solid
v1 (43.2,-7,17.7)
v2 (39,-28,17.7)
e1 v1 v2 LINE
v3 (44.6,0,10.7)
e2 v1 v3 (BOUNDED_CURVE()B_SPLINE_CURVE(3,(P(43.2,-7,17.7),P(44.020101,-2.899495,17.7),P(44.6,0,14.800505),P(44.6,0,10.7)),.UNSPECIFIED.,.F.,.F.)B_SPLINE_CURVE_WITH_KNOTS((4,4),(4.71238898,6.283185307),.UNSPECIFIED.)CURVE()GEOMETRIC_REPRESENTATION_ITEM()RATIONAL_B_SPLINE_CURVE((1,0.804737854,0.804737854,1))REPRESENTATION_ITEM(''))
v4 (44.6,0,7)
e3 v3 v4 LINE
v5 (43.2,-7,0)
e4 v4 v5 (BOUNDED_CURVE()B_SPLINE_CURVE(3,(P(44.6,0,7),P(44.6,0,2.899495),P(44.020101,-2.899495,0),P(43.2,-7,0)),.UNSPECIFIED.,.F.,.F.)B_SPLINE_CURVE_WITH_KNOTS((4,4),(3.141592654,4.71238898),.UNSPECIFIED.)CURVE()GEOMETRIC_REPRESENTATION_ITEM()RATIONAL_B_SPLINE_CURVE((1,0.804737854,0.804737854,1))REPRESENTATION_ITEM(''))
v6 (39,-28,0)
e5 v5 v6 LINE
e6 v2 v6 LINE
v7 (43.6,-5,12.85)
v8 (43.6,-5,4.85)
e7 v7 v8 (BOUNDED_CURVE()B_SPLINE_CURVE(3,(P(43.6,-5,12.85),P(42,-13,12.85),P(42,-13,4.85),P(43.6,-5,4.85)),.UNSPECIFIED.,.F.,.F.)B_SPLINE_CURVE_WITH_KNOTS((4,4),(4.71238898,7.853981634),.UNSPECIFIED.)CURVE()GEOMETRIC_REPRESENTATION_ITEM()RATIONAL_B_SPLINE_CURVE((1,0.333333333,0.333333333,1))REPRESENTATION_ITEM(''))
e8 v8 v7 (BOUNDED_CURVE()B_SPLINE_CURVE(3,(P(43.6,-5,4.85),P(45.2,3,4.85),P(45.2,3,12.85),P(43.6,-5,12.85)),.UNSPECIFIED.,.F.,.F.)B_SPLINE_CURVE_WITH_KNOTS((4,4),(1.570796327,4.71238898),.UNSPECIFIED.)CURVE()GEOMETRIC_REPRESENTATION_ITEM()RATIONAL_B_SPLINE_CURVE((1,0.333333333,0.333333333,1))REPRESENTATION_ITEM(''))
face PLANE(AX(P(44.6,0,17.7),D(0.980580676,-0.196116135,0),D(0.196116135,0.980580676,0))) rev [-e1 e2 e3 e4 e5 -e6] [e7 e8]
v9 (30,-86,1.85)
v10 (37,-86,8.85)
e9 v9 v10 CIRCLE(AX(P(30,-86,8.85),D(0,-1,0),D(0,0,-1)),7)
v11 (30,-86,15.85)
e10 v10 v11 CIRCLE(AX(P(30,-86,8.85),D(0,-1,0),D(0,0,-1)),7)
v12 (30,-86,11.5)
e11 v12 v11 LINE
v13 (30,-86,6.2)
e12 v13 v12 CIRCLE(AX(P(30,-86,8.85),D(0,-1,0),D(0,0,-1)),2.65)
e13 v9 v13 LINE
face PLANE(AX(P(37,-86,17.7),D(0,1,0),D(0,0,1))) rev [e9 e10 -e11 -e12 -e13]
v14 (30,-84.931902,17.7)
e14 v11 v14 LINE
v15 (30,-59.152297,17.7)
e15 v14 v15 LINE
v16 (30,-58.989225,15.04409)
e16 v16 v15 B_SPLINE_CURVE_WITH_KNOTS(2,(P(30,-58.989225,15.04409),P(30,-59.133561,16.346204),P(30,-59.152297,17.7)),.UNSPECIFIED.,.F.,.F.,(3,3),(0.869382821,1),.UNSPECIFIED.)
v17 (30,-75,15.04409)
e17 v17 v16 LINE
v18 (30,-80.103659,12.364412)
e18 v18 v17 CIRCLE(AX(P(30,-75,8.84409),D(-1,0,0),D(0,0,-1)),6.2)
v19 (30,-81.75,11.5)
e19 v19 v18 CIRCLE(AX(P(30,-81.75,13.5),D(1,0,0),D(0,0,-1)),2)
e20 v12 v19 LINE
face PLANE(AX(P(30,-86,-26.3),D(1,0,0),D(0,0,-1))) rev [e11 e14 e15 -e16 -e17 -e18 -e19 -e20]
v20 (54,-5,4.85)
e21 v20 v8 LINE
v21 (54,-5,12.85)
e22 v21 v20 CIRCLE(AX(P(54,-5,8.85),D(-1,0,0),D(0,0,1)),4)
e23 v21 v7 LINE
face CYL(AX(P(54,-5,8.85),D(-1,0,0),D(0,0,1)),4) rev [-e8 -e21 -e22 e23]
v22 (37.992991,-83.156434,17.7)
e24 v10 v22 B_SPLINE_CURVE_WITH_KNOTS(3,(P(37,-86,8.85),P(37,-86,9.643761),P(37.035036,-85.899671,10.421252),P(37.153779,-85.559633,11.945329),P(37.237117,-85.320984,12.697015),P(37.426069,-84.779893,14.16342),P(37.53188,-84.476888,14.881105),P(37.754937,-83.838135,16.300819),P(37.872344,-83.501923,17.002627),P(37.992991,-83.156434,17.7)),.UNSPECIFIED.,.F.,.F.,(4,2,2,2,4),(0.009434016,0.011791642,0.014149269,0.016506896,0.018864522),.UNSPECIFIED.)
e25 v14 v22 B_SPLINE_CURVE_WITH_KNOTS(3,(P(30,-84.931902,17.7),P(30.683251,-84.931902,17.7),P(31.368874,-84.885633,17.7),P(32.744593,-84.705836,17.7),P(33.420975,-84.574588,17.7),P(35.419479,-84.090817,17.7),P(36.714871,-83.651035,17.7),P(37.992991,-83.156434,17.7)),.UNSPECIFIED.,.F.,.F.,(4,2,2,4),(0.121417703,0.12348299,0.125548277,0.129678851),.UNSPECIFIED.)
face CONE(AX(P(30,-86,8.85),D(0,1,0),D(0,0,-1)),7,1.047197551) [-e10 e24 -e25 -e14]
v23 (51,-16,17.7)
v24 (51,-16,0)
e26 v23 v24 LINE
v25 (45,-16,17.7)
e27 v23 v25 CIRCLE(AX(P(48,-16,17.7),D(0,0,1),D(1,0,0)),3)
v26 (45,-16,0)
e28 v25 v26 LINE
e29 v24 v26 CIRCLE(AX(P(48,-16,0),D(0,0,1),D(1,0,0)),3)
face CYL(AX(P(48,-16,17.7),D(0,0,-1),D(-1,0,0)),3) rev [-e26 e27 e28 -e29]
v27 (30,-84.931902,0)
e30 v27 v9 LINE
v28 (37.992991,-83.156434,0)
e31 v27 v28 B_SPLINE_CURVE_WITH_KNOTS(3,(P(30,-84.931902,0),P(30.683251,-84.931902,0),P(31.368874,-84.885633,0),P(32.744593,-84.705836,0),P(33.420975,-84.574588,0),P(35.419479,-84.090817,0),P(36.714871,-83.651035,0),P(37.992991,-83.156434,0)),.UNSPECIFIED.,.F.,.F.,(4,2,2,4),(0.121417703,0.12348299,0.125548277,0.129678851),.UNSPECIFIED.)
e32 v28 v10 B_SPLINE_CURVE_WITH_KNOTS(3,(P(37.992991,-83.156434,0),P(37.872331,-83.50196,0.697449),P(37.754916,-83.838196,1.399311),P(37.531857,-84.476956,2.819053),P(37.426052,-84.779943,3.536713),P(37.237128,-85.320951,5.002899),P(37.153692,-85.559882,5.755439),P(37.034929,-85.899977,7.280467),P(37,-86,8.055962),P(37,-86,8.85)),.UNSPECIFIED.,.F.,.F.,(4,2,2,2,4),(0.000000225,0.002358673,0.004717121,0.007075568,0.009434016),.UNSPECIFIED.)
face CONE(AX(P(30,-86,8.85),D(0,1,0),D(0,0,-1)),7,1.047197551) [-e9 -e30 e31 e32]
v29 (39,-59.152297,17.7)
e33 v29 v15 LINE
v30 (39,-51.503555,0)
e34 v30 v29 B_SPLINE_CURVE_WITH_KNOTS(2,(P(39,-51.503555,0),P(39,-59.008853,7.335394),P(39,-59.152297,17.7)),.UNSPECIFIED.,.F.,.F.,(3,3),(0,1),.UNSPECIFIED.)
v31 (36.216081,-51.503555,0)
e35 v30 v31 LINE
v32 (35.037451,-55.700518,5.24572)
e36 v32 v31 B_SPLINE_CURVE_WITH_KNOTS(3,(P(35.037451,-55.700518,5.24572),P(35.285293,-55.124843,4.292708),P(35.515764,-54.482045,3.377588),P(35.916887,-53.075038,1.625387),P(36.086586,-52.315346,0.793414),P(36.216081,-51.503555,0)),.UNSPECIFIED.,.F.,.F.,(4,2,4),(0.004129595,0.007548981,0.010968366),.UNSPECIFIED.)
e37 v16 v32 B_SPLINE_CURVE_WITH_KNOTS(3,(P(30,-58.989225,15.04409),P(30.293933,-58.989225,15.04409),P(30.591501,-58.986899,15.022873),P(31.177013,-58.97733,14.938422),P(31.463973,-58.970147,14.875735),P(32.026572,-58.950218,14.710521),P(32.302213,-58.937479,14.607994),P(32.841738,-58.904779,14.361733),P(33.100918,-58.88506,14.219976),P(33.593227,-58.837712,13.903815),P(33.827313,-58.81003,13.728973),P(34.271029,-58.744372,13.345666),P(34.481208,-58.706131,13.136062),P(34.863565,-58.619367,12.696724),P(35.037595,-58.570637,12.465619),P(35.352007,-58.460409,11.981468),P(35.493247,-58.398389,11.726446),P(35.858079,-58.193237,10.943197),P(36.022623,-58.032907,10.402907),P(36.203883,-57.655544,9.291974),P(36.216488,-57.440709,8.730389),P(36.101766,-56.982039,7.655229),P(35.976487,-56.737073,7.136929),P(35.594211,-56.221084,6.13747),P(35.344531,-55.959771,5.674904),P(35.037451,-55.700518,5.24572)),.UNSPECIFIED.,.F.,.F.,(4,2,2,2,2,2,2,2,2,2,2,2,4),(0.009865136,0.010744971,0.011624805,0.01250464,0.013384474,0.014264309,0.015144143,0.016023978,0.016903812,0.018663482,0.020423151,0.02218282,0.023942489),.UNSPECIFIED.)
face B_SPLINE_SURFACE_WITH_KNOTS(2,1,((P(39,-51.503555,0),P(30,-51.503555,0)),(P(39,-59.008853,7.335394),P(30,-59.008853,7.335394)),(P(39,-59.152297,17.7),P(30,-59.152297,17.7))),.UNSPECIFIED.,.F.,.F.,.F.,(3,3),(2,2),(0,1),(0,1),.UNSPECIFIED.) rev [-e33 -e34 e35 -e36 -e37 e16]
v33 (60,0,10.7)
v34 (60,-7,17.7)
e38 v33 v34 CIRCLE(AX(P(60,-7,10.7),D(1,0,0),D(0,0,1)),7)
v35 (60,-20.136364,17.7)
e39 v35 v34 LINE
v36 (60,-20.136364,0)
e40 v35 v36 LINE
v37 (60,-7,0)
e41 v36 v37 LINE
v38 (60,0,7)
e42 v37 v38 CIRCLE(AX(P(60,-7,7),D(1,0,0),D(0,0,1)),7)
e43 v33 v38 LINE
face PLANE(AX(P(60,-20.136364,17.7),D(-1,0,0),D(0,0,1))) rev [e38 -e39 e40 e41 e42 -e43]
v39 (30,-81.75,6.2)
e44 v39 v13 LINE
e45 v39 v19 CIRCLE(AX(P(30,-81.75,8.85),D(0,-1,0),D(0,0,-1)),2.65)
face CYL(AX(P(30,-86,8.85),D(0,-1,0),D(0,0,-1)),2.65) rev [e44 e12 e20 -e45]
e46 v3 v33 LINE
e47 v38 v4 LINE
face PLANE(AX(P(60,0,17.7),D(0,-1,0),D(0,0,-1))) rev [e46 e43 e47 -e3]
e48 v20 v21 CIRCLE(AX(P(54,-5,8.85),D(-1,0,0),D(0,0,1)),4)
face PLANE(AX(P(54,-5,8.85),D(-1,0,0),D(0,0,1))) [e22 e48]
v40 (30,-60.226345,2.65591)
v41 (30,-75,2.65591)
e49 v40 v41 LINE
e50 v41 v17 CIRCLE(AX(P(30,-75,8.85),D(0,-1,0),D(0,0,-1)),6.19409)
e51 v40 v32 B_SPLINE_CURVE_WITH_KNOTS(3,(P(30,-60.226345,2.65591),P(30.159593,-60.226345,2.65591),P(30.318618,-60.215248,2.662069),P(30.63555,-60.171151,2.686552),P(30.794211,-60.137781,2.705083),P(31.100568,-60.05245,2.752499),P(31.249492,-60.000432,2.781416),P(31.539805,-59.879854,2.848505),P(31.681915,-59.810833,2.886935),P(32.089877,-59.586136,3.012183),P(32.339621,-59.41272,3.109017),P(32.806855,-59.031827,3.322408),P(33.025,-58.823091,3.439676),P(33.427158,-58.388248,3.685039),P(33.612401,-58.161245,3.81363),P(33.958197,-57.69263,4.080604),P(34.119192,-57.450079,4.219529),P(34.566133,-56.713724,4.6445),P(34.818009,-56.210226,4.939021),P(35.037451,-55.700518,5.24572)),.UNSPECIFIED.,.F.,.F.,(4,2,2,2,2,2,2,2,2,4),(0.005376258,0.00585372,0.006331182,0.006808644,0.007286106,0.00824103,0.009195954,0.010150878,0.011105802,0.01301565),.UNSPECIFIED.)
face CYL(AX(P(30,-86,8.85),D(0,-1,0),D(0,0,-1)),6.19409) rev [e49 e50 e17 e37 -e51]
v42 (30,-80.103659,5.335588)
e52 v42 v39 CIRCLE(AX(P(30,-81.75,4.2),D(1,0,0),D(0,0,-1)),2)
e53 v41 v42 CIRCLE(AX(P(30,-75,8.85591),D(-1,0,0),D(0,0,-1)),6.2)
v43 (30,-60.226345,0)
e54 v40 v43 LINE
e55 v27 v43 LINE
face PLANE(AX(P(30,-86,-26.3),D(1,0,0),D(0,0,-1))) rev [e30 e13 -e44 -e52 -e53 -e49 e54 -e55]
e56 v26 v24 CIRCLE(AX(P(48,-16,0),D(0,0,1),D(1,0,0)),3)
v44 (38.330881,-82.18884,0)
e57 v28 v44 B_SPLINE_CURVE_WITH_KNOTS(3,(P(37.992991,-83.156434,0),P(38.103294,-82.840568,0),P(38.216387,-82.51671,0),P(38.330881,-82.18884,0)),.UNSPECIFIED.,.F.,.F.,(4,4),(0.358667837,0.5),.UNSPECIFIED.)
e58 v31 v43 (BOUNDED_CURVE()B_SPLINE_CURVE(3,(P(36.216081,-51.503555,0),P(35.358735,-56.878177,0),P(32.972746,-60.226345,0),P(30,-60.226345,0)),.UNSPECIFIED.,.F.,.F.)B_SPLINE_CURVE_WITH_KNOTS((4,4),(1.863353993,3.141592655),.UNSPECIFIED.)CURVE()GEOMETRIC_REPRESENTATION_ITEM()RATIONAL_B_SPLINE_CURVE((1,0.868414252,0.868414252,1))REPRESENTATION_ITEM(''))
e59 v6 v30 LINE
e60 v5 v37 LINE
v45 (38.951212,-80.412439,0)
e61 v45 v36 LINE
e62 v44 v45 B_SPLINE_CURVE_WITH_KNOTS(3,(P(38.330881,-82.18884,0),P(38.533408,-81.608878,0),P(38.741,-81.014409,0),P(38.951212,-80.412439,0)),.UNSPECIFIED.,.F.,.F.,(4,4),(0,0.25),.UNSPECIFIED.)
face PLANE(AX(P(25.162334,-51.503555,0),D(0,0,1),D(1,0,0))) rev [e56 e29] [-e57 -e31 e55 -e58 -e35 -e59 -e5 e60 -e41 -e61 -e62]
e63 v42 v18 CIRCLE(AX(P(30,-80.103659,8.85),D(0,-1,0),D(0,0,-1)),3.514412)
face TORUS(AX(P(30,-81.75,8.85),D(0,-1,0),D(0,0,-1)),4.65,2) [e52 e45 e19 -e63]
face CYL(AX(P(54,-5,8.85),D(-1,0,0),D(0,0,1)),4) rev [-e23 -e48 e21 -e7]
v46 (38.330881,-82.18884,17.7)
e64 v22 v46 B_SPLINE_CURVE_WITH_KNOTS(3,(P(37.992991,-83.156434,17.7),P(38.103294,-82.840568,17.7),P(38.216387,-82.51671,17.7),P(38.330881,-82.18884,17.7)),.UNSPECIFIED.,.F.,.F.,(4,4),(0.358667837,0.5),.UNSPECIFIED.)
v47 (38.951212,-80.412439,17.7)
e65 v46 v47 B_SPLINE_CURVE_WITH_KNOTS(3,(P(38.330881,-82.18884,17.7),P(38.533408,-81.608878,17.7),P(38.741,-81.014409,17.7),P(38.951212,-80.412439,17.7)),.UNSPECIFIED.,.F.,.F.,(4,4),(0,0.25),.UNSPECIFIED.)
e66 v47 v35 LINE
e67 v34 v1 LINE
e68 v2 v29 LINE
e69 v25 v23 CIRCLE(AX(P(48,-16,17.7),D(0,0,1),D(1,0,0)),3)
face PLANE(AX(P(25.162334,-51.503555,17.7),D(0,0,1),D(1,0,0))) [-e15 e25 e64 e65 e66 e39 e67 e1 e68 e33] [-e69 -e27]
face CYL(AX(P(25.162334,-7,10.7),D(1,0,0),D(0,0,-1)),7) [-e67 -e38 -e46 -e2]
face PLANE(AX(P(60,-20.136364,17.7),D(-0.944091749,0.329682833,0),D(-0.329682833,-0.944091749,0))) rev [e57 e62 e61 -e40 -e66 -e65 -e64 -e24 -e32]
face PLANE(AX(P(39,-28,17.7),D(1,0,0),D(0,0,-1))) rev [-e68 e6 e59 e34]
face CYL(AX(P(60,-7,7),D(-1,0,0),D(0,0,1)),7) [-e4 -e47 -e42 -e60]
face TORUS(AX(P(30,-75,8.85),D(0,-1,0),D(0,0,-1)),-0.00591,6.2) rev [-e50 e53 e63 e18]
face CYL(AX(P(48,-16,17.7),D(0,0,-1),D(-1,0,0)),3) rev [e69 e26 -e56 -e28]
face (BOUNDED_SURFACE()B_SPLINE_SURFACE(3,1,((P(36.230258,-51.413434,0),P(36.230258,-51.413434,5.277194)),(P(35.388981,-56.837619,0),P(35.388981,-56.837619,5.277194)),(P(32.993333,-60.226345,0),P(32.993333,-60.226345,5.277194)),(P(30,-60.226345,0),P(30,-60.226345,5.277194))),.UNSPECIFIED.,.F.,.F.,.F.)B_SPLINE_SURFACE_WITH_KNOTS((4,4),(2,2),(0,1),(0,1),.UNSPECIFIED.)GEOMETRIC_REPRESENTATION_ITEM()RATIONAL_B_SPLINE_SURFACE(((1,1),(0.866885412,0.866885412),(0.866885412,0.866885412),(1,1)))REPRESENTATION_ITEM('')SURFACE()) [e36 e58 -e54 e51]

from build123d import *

# Parameters (mm, degrees)
SKETCH1_R                      = 3
BOSS_EXTRUDE2_DEPTH            = 17.7
CUT_EXTRUDE1_REACH             = 94.786
CUT_EXTRUDE1_DIRECTION_2_REACH = 94.786
SKETCH6_RX                     = 12.258033
SKETCH6_RY                     = 6.491927
CUT_EXTRUDE2_DEPTH             = 48.7
SKETCH7_R                      = 6.19409
CUT_EXTRUDE3_DEPTH             = 60.7
SKETCH8_R                      = 4
CUT_EXTRUDE4_DEPTH             = 48
FILLET1_R                      = 7
SKETCH10_OUTSIDE_W             = 249.546
SKETCH10_OUTSIDE_H             = 207.246
SKETCH10_OUTSIDE_R             = 7
CUT_EXTRUDE5_DEPTH             = 48
CUT_EXTRUDE5_TAPER             = 60
CUT_EXTRUDE8_DEPTH             = 44


with BuildPart() as part:
    # Sketch1 → Boss-Extrude2 (new body)
    with BuildSketch(Plane.XY):
        with BuildLine():
            Line((39, -51.503555), (34.837666, -51.503555))
            Line((34.837666, -51.503555), (25.162334, -51.503555))
            Line((25.162334, -51.503555), (21, -51.503555))
            Line((21, -51.503555), (21, -28.6))
            Line((21, -28.6), (15.376404, 0))
            Line((15.376404, 0), (0, 0))
            Line((0, 0), (0, -20.136364))
            Line((0, -20.136364), (21.048788, -80.412439))
            add(Edge.make_bspline(
                [(21.669142, -82.188906), (21.466678, -81.609123), (21.259066, -81.014599), (21.048788, -80.412439)],
                knots=[0.75, 0.75, 0.75, 0.75, 1, 1, 1, 1], degree=3))
            add(Edge.make_bspline(
                [(22.255532, -83.868113), (22.06924, -83.334643), (21.871606, -82.768689), (21.669142, -82.188906)],
                knots=[0.5, 0.5, 0.5, 0.5, 0.75, 0.75, 0.75, 0.75], degree=3))
            add(Edge.make_bspline(
                [(22.524034, -84.637007), (22.439154, -84.393941), (22.348677, -84.134848), (22.255532, -83.868113)],
                knots=[0.375, 0.375, 0.375, 0.375, 0.5, 0.5, 0.5, 0.5], degree=3))
            add(Edge.make_bspline(
                [(22.758263, -85.307753), (22.688292, -85.107381), (22.608914, -84.880073), (22.524034, -84.637007)],
                knots=[0.25, 0.25, 0.25, 0.25, 0.375, 0.375, 0.375, 0.375], degree=3))
            add(Edge.make_bspline(
                [(22.855261, -85.585519), (22.825847, -85.50129), (22.793248, -85.407938), (22.758263, -85.307753)],
                knots=[0.1875, 0.1875, 0.1875, 0.1875, 0.25, 0.25, 0.25, 0.25], degree=3))
            add(Edge.make_bspline(
                [(22.932474, -85.806631), (22.910958, -85.745015), (22.884674, -85.669748), (22.855261, -85.585519)],
                knots=[0.125, 0.125, 0.125, 0.125, 0.1875, 0.1875, 0.1875, 0.1875], degree=3))
            add(Edge.make_bspline(
                [(23, -86), (22.975508, -85.929864), (22.932474, -85.806631)],
                knots=[0, 0, 0, 0.125, 0.125, 0.125], degree=2))
            Line((23, -86), (37, -86))
            add(Edge.make_bspline(
                [(37.068167, -85.804796), (37.025162, -85.927946), (37, -86)],
                knots=[0.875, 0.875, 0.875, 1, 1, 1], degree=2))
            add(Edge.make_bspline(
                [(37.242328, -85.306061), (37.171936, -85.507639), (37.111171, -85.681646), (37.068167, -85.804796)],
                knots=[0.75, 0.75, 0.75, 0.75, 0.875, 0.875, 0.875, 0.875], degree=3))
            add(Edge.make_bspline(
                [(37.47673, -84.63482), (37.392157, -84.877005), (37.31272, -85.104482), (37.242328, -85.306061)],
                knots=[0.625, 0.625, 0.625, 0.625, 0.75, 0.75, 0.75, 0.75], degree=3))
            add(Edge.make_bspline(
                [(37.744144, -83.869041), (37.651111, -84.135454), (37.561302, -84.392634), (37.47673, -84.63482)],
                knots=[0.5, 0.5, 0.5, 0.5, 0.625, 0.625, 0.625, 0.625], degree=3))
            add(Edge.make_bspline(
                [(38.330881, -82.18884), (38.128355, -82.768803), (37.930211, -83.336215), (37.744144, -83.869041)],
                knots=[0.25, 0.25, 0.25, 0.25, 0.5, 0.5, 0.5, 0.5], degree=3))
            add(Edge.make_bspline(
                [(38.951212, -80.412439), (38.741, -81.014409), (38.533408, -81.608878), (38.330881, -82.18884)],
                knots=[0, 0, 0, 0, 0.25, 0.25, 0.25, 0.25], degree=3))
            Line((38.951212, -80.412439), (60, -20.136364))
            Line((60, -20.136364), (60, 0))
            Line((60, 0), (44.6, 0))
            Line((44.6, 0), (39, -28))
            Line((39, -28), (39, -51.503555))
        make_face()
        with Locations((48, -16)):
            Circle(SKETCH1_R, mode=Mode.SUBTRACT)
        with Locations((12, -16)):
            Circle(SKETCH1_R, mode=Mode.SUBTRACT)
    extrude(amount=BOSS_EXTRUDE2_DEPTH)

    # Sketch2 → Cut-Revolve2 (revolve, cut)
    with BuildSketch(Plane.ZY.offset(-30), mode=Mode.PRIVATE) as cut_revolve2_sk:
        with BuildLine():
            ThreePointArc((11.5, -81.75), (11.729241, -80.820262), (12.364412, -80.103659))
            ThreePointArc((12.364412, -80.103659), (14.333443, -77.882187), (15.04409, -75))
            Line((15.04409, -75), (15.04409, -57.48))
            Line((15.04409, -57.48), (8.85, -57.48))
            Line((8.85, -57.48), (8.85, -86))
            Line((8.85, -86), (11.5, -86))
            Line((11.5, -86), (11.5, -81.75))
        make_face()
    revolve(cut_revolve2_sk.sketch.rotate(Axis((30, -86, 8.85), (0, 1, 0)), 180), axis=Axis((30, -86, 8.85), (0, 1, 0)), mode=Mode.SUBTRACT)

    # Cut-Extrude1: up to this face of the body (flat: up to its plane)
    cut_extrude1_end = Plane(part.part.faces().sort_by_distance((39, -39.751777, 8.85))[0])
    # Sketch3 → Cut-Extrude1 (cut, up to the picked face)
    with BuildSketch(Plane.ZY.offset(-30), mode=Mode.PRIVATE) as cut_extrude1_sk1:
        with BuildLine():
            Line((0, -51.503555), (17.7, -51.503555))
            Line((17.7, -51.503555), (17.7, -59.152297))
            add(Edge.make_bspline(
                [(17.7, -59.152297), (7.335394, -59.008853), (0, -51.503555)],
                knots=[0, 0, 0, 1, 1, 1], degree=2))
        make_face()
    cut_extrude1_tool1 = split(extrude(cut_extrude1_sk1.sketch, amount=-CUT_EXTRUDE1_REACH, mode=Mode.PRIVATE), bisect_by=cut_extrude1_end, keep=Keep.BOTH, mode=Mode.PRIVATE)
    add(cut_extrude1_tool1.solids().sort_by(Axis((30, -54.604638, 10.907898), (1, 0, 0)))[0], mode=Mode.SUBTRACT)

    # Cut-Extrude1 direction 2: up to this face of the body (flat: up to its plane)
    cut_extrude1_direction_2_end = Plane(part.part.faces().sort_by_distance((21, -40.051777, 8.85))[0])
    # Sketch3 → Cut-Extrude1 direction 2 (cut, up to the picked face)
    with BuildSketch(Plane.ZY.offset(-30), mode=Mode.PRIVATE) as cut_extrude1_direction_2_sk1:
        with BuildLine():
            Line((0, -51.503555), (17.7, -51.503555))
            Line((17.7, -51.503555), (17.7, -59.152297))
            add(Edge.make_bspline(
                [(17.7, -59.152297), (7.335394, -59.008853), (0, -51.503555)],
                knots=[0, 0, 0, 1, 1, 1], degree=2))
        make_face()
    cut_extrude1_direction_2_tool1 = split(extrude(cut_extrude1_direction_2_sk1.sketch, amount=CUT_EXTRUDE1_DIRECTION_2_REACH, mode=Mode.PRIVATE), bisect_by=cut_extrude1_direction_2_end, keep=Keep.BOTH, mode=Mode.PRIVATE)
    add(cut_extrude1_direction_2_tool1.solids().sort_by(Axis((30, -54.604638, 10.907898), (-1, 0, 0)))[0], mode=Mode.SUBTRACT)

    # Sketch6 → Cut-Extrude2 (cut)
    with BuildSketch(Plane(origin=(0, 0, 8.85), x_dir=(-1, 0, 0), z_dir=(0, 0, -1))):
        with Locations(Location((-30, -47.968312), (0, 0, 90))):
            Ellipse(SKETCH6_RX, SKETCH6_RY)
    extrude(amount=CUT_EXTRUDE2_DEPTH, mode=Mode.SUBTRACT)

    # Sketch7 → Cut-Extrude3 (cut)
    with BuildSketch(Plane(origin=(0, 0, 0), x_dir=(1, 0, 0), z_dir=(0, 1, 0))):
        with Locations(Location((30, -8.85, 0), (0, 0, 90))):
            Circle(SKETCH7_R)
    extrude(amount=-CUT_EXTRUDE3_DEPTH, mode=Mode.SUBTRACT)

    # Sketch8 → Cut-Extrude4 (cut)
    with BuildSketch(Plane.ZY.offset(-6)):
        with Locations((8.85, -5)):
            Circle(SKETCH8_R)
    extrude(amount=-CUT_EXTRUDE4_DEPTH, mode=Mode.SUBTRACT)

    # Fillet1
    fillet1_edges = [part.edges().sort_by_distance(p)[0] for p in [
        (7.688202, 0, 17.7),
        (52.3, 0, 0),
        (7.688202, 0, 0),
        (52.3, 0, 17.7),
    ]]
    fillet(fillet1_edges, radius=FILLET1_R)

    # Sketch10 outside → Cut-Extrude5 (cut)
    with BuildSketch(Plane.XZ.offset(86)):
        with Locations((30, 8.85)):
            Rectangle(SKETCH10_OUTSIDE_W, SKETCH10_OUTSIDE_H)
        with Locations((30, 8.85)):
            Circle(SKETCH10_OUTSIDE_R, mode=Mode.SUBTRACT)
    extrude(amount=-CUT_EXTRUDE5_DEPTH, taper=CUT_EXTRUDE5_TAPER, mode=Mode.SUBTRACT)

    # Sketch12 → Cut-Extrude8 (cut)
    with BuildSketch(Plane.XY.offset(17.7)):
        Polygon((30, -86), (30, 13.730719), (-24.441977, 10.861444), (-8.282064, -99.477746), align=None)
    extrude(amount=-CUT_EXTRUDE8_DEPTH, mode=Mode.SUBTRACT)


solid = part.part
